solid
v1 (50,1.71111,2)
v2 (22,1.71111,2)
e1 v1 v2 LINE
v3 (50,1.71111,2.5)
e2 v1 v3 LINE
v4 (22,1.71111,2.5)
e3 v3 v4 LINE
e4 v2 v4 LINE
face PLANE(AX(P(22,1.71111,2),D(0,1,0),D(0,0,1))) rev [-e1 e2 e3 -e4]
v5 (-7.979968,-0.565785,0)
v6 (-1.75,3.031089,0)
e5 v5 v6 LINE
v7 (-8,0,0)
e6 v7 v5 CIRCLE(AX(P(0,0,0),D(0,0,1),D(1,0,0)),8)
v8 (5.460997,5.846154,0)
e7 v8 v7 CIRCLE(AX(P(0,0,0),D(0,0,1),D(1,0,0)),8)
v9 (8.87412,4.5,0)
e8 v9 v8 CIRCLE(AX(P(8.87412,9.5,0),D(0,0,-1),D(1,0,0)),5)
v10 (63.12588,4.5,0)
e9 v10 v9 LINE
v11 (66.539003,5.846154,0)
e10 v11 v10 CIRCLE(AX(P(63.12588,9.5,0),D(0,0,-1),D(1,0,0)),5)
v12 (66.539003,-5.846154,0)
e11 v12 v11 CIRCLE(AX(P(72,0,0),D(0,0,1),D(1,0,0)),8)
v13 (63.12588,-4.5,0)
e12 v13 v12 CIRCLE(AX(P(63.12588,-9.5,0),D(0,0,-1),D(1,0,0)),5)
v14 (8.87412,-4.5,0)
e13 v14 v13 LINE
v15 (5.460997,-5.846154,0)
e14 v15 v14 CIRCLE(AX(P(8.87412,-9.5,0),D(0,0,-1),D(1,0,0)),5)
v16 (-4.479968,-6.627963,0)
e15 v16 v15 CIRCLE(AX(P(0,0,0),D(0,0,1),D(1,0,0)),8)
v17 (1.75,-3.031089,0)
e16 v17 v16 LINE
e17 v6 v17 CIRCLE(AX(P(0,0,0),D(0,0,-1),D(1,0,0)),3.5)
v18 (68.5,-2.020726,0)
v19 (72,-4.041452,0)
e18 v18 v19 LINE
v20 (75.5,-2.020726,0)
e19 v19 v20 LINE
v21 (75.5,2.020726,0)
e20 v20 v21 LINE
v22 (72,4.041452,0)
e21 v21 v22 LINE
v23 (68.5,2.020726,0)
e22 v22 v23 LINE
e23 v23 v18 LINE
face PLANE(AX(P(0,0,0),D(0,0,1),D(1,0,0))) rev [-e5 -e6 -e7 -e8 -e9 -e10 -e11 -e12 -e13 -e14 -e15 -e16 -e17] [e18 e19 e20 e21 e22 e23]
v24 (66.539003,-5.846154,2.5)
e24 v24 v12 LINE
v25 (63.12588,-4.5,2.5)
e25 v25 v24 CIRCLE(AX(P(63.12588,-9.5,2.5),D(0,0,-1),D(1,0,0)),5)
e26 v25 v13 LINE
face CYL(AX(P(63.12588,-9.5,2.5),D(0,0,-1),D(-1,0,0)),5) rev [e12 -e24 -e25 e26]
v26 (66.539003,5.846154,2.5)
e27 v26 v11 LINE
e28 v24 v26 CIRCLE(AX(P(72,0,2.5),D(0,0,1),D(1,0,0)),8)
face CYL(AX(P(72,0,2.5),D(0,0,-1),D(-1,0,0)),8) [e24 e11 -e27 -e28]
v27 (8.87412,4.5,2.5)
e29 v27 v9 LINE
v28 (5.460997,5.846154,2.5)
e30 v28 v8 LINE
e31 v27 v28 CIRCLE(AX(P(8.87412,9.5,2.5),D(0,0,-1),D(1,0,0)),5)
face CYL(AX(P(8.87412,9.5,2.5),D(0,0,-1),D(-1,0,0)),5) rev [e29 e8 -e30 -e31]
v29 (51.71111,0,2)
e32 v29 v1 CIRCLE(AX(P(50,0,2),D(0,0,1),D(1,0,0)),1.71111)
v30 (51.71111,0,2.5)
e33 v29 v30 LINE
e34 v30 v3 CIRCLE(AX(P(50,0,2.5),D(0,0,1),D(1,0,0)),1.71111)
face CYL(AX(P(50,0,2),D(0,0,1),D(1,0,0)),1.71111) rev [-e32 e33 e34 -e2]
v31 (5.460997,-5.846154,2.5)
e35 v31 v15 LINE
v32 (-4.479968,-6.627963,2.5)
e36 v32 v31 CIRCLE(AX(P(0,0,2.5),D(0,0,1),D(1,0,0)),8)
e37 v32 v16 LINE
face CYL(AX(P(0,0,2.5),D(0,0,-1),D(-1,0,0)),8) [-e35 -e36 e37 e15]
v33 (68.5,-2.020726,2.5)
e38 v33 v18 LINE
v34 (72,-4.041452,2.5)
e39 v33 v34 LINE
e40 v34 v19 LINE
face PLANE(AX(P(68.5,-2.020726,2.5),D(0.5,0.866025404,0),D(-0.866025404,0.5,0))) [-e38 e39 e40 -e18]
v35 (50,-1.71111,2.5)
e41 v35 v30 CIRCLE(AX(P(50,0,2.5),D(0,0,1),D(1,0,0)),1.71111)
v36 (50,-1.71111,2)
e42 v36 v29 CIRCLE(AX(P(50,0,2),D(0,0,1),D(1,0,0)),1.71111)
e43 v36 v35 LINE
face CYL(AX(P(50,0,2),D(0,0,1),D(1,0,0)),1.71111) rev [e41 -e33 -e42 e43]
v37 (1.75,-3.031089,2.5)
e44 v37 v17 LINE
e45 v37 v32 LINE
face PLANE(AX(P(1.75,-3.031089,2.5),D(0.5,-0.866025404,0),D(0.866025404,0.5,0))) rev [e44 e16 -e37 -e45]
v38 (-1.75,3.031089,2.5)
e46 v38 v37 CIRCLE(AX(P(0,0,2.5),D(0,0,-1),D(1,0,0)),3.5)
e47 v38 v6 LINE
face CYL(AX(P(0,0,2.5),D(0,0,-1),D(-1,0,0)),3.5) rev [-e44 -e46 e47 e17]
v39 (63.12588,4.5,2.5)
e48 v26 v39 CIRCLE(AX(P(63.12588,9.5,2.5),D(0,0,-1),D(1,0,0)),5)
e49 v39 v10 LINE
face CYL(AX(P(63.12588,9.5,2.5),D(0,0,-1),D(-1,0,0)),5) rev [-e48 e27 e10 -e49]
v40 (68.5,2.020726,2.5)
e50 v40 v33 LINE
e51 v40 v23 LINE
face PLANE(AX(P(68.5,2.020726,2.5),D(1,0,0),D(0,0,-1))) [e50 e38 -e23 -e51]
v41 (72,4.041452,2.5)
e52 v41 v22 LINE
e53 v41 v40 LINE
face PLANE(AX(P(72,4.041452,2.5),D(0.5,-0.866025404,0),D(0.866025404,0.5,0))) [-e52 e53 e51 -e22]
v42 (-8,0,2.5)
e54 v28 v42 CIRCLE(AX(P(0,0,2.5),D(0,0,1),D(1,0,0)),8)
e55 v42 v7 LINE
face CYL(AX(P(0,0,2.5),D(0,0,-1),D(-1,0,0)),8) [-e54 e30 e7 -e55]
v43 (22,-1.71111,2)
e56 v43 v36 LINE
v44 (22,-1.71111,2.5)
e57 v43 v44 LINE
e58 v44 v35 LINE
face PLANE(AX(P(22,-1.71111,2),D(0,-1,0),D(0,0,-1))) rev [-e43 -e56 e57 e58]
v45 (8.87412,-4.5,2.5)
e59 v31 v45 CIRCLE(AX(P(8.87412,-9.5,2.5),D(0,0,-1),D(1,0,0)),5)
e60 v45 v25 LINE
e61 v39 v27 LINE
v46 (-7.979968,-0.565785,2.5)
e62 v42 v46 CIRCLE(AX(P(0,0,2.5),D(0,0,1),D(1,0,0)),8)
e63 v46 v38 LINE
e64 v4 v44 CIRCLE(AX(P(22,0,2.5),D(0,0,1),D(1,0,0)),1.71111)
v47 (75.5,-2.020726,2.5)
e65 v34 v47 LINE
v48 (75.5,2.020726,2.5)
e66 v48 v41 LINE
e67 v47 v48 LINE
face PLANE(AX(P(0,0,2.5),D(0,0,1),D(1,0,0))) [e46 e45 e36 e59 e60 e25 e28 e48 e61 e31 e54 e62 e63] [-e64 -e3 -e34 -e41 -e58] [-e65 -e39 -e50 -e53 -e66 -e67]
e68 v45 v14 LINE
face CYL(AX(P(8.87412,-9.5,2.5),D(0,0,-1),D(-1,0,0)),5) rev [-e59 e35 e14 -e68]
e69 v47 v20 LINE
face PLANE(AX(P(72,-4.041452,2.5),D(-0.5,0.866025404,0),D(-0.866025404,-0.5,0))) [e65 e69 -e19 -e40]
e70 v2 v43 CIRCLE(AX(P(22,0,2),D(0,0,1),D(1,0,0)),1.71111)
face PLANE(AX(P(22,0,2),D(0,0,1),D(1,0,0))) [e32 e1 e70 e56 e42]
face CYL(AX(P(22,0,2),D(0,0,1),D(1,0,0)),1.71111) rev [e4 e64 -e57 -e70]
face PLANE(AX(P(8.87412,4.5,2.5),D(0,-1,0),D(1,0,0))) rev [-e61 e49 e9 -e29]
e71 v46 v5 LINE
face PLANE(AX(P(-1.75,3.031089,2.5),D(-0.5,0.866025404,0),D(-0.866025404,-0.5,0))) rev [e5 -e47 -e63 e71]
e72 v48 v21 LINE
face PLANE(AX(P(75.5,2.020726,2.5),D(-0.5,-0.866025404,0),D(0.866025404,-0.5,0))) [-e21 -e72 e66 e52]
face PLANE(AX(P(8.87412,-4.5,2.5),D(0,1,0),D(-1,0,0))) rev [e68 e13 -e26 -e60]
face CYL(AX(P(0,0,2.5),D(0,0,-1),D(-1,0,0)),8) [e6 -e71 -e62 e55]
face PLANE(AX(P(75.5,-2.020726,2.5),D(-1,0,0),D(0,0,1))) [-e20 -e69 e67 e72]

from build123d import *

# Parameters (mm, degrees)
SPANNER_BODY_2_5MM_DEPTH       = 2.5
HANDLE_SLOT_RECESS_0_5MM_DEPTH = 0.5


with BuildPart() as part:
    # Spanner Outline Sketch → Spanner Body 2.5mm (new body)
    with BuildSketch(Plane.XY):
        with BuildLine():
            Line((8.874119675, -4.5), (63.125880325, -4.5))
            ThreePointArc((63.125880325, -4.5), (64.96037879, -4.848697453), (66.539003277, -5.846153846))
            ThreePointArc((66.539003277, -5.846153846), (80, 0), (66.539003277, 5.846153846))
            ThreePointArc((66.539003277, 5.846153846), (64.96037879, 4.848697453), (63.125880325, 4.5))
            Line((63.125880325, 4.5), (8.874119675, 4.5))
            ThreePointArc((8.874119675, 4.5), (7.03962121, 4.848697453), (5.460996723, 5.846153846))
            ThreePointArc((5.460996723, 5.846153846), (-3.444494595, 7.220488694), (-7.979967897, -0.565784729))
            Line((-7.979967897, -0.565784729), (-1.75, 3.031088913))
            ThreePointArc((-1.75, 3.031088913), (3.031088913, 1.75), (1.75, -3.031088913))
            Line((1.75, -3.031088913), (-4.479967897, -6.627962556))
            ThreePointArc((-4.479967897, -6.627962556), (0.627224524, -7.975373935), (5.460996723, -5.846153846))
            ThreePointArc((5.460996723, -5.846153846), (7.03962121, -4.848697453), (8.874119675, -4.5))
        make_face()
        Polygon((75.5, -2.020725942), (75.5, 2.020725942), (72, 4.041451884), (68.5, 2.020725942), (68.5, -2.020725942), (72, -4.041451884), align=None, mode=Mode.SUBTRACT)
    extrude(amount=SPANNER_BODY_2_5MM_DEPTH)

    # Handle Slot Sketch → Handle Slot Recess 0.5mm (cut)
    with BuildSketch(Plane.XY.offset(2.5)):
        with BuildLine():
            Line((22, 1.71110999), (50, 1.71110999))
            ThreePointArc((50, 1.71110999), (51.71110999, 0), (50, -1.71110999))
            Line((50, -1.71110999), (22, -1.71110999))
            ThreePointArc((22, -1.71110999), (20.28889001, 0), (22, 1.71110999))
        make_face()
    extrude(amount=-HANDLE_SLOT_RECESS_0_5MM_DEPTH, mode=Mode.SUBTRACT)


solid = part.part
